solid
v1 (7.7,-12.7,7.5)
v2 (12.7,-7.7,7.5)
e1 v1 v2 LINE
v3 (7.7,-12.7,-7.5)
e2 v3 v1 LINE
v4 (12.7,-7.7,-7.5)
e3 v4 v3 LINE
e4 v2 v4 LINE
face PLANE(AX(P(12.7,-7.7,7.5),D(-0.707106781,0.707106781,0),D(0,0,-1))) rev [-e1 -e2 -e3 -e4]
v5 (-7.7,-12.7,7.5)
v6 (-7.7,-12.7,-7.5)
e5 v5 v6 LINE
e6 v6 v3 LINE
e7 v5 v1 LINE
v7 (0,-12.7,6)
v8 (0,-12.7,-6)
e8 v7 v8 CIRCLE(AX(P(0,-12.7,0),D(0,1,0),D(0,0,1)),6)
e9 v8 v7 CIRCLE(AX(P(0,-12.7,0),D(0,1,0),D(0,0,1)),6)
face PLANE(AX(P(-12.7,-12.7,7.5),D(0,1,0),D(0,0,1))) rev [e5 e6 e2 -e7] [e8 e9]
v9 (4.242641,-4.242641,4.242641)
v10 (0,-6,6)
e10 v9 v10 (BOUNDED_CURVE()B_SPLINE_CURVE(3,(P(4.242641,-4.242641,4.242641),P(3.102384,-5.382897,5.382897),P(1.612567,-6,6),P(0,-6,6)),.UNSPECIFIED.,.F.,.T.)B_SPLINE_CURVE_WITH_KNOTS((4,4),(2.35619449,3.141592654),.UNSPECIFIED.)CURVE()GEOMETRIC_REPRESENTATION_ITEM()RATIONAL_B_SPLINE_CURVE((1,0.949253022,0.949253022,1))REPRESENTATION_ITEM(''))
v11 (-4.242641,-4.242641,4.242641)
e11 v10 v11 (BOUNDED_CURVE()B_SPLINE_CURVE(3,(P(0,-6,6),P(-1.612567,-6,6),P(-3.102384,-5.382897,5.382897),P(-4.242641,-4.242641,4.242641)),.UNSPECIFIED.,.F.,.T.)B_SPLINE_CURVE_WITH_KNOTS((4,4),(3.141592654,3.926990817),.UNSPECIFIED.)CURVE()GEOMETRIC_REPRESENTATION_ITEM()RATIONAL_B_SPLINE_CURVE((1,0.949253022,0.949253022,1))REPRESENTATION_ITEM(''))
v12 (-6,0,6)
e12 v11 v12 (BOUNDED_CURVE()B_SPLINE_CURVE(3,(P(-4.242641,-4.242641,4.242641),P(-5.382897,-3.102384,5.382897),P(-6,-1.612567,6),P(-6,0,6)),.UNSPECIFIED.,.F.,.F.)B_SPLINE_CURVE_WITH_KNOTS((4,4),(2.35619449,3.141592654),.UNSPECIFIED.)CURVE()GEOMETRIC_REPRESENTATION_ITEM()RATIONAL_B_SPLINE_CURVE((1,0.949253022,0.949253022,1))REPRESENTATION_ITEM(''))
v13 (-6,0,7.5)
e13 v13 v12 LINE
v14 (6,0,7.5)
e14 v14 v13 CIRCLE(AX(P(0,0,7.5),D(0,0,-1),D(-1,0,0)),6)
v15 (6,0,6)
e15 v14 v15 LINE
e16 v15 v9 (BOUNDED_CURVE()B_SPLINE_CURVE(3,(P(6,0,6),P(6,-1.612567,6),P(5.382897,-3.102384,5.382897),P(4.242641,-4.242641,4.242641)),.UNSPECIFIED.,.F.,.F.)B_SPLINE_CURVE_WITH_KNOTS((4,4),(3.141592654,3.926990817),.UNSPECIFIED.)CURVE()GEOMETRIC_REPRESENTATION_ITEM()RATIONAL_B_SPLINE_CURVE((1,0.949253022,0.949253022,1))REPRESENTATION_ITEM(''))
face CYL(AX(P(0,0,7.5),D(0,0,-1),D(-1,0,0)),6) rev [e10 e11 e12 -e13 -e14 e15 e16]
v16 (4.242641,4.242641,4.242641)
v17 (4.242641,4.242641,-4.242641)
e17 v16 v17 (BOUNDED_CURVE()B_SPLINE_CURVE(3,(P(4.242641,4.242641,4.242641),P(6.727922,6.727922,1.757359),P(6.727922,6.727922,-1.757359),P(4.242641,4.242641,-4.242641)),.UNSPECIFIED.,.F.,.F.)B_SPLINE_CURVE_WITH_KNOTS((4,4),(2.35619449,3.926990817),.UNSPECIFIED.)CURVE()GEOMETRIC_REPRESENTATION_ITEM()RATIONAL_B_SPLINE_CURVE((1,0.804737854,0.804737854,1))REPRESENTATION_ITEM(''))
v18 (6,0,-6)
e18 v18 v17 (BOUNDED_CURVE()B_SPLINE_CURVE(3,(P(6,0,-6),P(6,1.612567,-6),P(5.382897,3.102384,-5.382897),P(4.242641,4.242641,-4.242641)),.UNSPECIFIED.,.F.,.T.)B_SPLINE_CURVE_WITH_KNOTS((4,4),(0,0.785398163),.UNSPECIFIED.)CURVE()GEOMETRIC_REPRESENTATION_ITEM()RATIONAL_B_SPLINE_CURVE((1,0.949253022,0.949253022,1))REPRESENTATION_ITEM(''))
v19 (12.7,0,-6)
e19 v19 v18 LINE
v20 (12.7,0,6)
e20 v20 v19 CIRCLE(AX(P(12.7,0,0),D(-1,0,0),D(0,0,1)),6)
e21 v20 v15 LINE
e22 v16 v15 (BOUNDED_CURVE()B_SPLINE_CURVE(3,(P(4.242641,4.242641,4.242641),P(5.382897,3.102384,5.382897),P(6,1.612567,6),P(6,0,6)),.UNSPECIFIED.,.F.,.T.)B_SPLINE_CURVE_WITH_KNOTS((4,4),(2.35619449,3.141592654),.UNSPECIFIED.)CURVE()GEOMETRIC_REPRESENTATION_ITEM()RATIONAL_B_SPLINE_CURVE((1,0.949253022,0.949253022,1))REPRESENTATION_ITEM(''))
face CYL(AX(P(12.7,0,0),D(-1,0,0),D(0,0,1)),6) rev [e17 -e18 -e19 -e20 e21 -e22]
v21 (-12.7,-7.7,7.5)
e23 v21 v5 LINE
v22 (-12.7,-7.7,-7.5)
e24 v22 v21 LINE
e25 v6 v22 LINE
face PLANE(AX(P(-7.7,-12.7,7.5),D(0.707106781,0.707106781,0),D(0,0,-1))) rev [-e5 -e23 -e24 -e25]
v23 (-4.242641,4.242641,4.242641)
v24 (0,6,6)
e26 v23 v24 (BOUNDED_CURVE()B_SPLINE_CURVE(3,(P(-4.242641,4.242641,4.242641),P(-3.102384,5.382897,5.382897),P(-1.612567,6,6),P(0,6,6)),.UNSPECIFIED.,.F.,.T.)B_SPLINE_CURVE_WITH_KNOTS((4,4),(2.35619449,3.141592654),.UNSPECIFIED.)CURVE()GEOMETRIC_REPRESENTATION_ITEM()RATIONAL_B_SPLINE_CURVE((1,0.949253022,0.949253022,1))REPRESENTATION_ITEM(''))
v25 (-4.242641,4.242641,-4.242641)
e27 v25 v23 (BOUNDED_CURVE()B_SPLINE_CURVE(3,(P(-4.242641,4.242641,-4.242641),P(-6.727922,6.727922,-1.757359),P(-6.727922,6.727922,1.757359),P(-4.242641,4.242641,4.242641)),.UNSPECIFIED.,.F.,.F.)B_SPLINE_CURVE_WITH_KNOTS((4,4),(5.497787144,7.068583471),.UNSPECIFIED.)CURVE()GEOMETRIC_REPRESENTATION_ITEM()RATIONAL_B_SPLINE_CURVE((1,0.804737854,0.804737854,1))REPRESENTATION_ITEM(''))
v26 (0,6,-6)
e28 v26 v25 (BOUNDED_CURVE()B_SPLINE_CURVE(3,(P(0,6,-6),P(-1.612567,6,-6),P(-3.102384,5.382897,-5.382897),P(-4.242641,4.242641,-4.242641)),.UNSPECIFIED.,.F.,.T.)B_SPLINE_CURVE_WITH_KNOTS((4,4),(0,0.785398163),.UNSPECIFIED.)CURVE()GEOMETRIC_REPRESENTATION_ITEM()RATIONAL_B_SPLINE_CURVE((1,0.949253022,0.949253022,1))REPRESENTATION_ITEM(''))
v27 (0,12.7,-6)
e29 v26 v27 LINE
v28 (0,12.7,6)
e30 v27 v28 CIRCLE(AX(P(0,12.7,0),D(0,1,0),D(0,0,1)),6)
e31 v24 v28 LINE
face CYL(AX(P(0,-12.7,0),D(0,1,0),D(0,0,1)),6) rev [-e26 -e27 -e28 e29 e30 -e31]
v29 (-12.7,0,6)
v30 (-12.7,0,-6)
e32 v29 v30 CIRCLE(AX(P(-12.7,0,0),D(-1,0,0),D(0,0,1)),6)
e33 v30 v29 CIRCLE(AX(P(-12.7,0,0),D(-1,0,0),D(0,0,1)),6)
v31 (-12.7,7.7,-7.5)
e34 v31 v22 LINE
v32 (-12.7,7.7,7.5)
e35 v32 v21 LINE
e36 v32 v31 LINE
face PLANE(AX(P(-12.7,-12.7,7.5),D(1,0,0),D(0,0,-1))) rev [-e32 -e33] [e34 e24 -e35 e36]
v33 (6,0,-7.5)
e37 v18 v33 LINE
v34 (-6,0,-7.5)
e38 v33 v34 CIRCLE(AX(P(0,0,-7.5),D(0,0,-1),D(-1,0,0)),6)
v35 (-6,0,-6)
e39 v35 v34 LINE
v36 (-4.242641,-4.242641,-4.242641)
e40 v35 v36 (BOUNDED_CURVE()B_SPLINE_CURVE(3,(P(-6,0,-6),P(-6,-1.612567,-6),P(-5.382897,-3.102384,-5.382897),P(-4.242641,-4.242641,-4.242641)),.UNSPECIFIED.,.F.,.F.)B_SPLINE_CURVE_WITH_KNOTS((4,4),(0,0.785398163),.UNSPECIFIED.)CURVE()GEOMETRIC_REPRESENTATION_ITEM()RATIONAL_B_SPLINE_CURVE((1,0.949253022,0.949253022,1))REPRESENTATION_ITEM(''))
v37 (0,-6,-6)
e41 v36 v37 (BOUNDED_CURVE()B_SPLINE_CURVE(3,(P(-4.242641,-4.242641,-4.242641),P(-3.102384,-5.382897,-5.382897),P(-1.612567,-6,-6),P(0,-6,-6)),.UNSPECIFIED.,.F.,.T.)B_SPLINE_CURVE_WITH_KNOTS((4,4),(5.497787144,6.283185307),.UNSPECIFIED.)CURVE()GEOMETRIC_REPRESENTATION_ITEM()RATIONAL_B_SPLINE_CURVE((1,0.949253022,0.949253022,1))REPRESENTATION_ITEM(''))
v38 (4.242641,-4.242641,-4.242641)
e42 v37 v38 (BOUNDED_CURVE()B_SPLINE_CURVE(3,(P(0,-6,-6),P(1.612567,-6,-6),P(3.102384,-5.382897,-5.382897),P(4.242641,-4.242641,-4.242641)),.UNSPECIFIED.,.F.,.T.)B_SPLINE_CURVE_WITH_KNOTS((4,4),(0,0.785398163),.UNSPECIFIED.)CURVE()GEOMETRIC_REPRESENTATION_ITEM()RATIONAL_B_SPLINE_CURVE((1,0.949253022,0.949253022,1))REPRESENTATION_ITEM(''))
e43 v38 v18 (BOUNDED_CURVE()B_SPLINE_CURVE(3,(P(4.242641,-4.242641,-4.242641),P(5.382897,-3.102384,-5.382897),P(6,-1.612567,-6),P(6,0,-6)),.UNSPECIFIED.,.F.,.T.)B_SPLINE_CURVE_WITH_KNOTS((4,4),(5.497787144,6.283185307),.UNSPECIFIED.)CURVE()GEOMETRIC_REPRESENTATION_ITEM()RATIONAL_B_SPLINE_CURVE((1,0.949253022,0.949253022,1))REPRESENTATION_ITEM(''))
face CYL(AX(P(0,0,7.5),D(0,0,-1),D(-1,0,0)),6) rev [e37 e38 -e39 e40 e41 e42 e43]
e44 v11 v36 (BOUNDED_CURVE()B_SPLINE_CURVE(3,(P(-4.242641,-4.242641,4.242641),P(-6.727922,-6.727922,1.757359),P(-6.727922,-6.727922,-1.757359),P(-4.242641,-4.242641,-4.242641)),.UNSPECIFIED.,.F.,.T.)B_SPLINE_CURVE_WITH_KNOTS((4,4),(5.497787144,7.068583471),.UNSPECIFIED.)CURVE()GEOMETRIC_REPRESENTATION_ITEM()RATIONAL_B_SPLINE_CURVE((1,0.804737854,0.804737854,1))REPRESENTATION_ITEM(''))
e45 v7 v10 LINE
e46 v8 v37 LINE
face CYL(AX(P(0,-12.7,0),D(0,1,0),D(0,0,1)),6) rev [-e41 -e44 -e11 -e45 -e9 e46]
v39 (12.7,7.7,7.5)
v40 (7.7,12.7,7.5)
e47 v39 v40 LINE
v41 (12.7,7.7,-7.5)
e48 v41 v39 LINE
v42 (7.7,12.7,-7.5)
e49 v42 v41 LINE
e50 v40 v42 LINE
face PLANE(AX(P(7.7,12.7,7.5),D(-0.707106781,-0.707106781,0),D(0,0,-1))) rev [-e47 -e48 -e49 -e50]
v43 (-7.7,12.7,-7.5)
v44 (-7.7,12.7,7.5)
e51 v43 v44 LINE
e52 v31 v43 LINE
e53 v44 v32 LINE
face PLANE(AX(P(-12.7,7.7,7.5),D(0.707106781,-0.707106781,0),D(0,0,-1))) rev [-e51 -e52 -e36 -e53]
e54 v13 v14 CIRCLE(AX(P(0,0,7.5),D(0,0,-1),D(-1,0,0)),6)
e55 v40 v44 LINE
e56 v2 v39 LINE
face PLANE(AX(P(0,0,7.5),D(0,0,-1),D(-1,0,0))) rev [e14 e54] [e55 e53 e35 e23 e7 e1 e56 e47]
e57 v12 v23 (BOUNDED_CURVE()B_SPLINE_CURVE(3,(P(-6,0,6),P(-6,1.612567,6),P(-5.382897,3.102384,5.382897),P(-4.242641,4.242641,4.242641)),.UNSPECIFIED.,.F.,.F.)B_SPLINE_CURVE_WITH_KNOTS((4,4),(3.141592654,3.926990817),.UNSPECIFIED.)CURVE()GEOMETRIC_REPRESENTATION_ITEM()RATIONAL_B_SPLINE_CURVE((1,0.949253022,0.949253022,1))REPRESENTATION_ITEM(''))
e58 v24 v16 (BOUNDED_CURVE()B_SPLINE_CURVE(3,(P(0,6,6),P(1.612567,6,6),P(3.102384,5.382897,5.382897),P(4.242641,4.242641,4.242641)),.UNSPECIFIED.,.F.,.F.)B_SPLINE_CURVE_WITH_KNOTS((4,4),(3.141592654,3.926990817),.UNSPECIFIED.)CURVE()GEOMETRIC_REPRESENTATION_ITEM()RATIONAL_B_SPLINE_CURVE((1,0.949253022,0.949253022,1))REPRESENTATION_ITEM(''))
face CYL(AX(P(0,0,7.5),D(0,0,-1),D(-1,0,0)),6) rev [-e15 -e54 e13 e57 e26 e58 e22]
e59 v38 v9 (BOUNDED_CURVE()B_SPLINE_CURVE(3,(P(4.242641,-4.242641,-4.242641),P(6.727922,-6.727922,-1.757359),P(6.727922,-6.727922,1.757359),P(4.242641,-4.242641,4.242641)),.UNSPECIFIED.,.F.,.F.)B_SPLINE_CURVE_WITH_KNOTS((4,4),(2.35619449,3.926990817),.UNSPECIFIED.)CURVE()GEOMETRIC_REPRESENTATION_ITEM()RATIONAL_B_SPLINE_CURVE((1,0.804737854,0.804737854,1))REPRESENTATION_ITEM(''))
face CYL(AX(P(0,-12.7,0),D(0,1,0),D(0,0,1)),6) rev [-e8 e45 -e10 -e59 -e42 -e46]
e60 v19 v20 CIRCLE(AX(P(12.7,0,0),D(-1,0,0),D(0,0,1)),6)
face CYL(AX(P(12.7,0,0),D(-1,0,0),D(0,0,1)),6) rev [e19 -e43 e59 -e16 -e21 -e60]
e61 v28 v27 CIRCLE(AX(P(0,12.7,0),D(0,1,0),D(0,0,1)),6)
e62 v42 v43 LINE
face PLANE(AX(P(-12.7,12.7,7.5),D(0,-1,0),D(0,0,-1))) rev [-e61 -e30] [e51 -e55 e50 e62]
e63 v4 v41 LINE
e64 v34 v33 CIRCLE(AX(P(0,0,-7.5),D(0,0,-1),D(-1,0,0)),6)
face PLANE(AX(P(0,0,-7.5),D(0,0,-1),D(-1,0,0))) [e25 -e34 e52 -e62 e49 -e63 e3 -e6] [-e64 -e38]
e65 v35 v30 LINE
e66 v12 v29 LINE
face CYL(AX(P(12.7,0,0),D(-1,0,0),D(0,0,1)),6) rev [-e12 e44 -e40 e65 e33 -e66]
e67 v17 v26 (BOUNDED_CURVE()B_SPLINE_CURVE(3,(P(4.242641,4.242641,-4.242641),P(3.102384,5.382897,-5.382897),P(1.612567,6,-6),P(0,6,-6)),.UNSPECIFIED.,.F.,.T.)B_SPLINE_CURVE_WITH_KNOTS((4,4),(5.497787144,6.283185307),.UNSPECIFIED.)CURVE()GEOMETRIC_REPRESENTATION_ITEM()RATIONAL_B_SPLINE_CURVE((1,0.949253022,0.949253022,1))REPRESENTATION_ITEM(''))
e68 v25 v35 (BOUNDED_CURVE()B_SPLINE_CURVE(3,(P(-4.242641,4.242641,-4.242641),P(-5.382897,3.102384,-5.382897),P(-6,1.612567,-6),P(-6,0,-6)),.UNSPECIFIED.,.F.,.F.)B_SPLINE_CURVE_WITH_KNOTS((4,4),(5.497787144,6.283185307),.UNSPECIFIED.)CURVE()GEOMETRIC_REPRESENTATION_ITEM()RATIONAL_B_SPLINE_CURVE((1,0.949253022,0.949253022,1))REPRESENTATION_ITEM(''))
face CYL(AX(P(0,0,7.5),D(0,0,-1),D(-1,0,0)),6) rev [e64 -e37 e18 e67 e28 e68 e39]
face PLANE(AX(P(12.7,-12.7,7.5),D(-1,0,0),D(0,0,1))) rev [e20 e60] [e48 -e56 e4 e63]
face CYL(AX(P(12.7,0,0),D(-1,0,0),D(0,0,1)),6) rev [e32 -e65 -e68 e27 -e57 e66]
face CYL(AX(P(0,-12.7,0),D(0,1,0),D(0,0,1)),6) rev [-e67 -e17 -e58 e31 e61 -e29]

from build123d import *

# Parameters (mm, degrees)
NUT_BODY_PROFILE_W     = 25.4
NUT_BODY_PROFILE_H     = 25.4
NUT_BODY_DEPTH         = 7.5
EDGE_CHAMFERS_5MM_SIZE = 5
AXIAL_BORE_PROFILE_R   = 6
AXIAL_BORE_12_DEPTH    = 15
CROSS_BORE_A_PROFILE_R = 6
CROSS_BORE_A_12_DEPTH  = 30.37175514
CROSS_BORE_B_PROFILE_R = 6
CROSS_BORE_B_12_DEPTH  = 30.37175514


with BuildPart() as part:
    # Nut Body Profile → Nut Body (new, symmetric)
    with BuildSketch(Plane.XY):
        Rectangle(NUT_BODY_PROFILE_W, NUT_BODY_PROFILE_H)
    extrude(amount=NUT_BODY_DEPTH, both=True)

    # Edge Chamfers 5mm
    edge_chamfers_5mm_edges = [part.edges().sort_by_distance(p)[0] for p in [
        (12.7, -12.7, 0),
        (-12.7, -12.7, 0),
        (-12.7, 12.7, 0),
        (12.7, 12.7, 0),
    ]]
    chamfer(edge_chamfers_5mm_edges, length=EDGE_CHAMFERS_5MM_SIZE)

    # Axial Bore Profile → Axial Bore Ø12 (cut)
    with BuildSketch(Plane(origin=(0, 0, -7.5), x_dir=(-1, 0, 0), z_dir=(0, 0, -1))):
        Circle(AXIAL_BORE_PROFILE_R)
    extrude(amount=-AXIAL_BORE_12_DEPTH, mode=Mode.SUBTRACT)

    # Cross Bore A Profile → Cross Bore A Ø12 (cut, through all)
    with BuildSketch(Plane.ZY.offset(12.7)):
        Circle(CROSS_BORE_A_PROFILE_R)
    extrude(amount=-CROSS_BORE_A_12_DEPTH, mode=Mode.SUBTRACT)

    # Cross Bore B Profile → Cross Bore B Ø12 (cut, through all)
    with BuildSketch(Plane(origin=(0, 12.7, 0), x_dir=(1, 0, 0), z_dir=(0, 1, 0))):
        with Locations(Location((0, 0, 0), (0, 0, 270))):
            Circle(CROSS_BORE_B_PROFILE_R)
    extrude(amount=-CROSS_BORE_B_12_DEPTH, mode=Mode.SUBTRACT)


solid = part.part
